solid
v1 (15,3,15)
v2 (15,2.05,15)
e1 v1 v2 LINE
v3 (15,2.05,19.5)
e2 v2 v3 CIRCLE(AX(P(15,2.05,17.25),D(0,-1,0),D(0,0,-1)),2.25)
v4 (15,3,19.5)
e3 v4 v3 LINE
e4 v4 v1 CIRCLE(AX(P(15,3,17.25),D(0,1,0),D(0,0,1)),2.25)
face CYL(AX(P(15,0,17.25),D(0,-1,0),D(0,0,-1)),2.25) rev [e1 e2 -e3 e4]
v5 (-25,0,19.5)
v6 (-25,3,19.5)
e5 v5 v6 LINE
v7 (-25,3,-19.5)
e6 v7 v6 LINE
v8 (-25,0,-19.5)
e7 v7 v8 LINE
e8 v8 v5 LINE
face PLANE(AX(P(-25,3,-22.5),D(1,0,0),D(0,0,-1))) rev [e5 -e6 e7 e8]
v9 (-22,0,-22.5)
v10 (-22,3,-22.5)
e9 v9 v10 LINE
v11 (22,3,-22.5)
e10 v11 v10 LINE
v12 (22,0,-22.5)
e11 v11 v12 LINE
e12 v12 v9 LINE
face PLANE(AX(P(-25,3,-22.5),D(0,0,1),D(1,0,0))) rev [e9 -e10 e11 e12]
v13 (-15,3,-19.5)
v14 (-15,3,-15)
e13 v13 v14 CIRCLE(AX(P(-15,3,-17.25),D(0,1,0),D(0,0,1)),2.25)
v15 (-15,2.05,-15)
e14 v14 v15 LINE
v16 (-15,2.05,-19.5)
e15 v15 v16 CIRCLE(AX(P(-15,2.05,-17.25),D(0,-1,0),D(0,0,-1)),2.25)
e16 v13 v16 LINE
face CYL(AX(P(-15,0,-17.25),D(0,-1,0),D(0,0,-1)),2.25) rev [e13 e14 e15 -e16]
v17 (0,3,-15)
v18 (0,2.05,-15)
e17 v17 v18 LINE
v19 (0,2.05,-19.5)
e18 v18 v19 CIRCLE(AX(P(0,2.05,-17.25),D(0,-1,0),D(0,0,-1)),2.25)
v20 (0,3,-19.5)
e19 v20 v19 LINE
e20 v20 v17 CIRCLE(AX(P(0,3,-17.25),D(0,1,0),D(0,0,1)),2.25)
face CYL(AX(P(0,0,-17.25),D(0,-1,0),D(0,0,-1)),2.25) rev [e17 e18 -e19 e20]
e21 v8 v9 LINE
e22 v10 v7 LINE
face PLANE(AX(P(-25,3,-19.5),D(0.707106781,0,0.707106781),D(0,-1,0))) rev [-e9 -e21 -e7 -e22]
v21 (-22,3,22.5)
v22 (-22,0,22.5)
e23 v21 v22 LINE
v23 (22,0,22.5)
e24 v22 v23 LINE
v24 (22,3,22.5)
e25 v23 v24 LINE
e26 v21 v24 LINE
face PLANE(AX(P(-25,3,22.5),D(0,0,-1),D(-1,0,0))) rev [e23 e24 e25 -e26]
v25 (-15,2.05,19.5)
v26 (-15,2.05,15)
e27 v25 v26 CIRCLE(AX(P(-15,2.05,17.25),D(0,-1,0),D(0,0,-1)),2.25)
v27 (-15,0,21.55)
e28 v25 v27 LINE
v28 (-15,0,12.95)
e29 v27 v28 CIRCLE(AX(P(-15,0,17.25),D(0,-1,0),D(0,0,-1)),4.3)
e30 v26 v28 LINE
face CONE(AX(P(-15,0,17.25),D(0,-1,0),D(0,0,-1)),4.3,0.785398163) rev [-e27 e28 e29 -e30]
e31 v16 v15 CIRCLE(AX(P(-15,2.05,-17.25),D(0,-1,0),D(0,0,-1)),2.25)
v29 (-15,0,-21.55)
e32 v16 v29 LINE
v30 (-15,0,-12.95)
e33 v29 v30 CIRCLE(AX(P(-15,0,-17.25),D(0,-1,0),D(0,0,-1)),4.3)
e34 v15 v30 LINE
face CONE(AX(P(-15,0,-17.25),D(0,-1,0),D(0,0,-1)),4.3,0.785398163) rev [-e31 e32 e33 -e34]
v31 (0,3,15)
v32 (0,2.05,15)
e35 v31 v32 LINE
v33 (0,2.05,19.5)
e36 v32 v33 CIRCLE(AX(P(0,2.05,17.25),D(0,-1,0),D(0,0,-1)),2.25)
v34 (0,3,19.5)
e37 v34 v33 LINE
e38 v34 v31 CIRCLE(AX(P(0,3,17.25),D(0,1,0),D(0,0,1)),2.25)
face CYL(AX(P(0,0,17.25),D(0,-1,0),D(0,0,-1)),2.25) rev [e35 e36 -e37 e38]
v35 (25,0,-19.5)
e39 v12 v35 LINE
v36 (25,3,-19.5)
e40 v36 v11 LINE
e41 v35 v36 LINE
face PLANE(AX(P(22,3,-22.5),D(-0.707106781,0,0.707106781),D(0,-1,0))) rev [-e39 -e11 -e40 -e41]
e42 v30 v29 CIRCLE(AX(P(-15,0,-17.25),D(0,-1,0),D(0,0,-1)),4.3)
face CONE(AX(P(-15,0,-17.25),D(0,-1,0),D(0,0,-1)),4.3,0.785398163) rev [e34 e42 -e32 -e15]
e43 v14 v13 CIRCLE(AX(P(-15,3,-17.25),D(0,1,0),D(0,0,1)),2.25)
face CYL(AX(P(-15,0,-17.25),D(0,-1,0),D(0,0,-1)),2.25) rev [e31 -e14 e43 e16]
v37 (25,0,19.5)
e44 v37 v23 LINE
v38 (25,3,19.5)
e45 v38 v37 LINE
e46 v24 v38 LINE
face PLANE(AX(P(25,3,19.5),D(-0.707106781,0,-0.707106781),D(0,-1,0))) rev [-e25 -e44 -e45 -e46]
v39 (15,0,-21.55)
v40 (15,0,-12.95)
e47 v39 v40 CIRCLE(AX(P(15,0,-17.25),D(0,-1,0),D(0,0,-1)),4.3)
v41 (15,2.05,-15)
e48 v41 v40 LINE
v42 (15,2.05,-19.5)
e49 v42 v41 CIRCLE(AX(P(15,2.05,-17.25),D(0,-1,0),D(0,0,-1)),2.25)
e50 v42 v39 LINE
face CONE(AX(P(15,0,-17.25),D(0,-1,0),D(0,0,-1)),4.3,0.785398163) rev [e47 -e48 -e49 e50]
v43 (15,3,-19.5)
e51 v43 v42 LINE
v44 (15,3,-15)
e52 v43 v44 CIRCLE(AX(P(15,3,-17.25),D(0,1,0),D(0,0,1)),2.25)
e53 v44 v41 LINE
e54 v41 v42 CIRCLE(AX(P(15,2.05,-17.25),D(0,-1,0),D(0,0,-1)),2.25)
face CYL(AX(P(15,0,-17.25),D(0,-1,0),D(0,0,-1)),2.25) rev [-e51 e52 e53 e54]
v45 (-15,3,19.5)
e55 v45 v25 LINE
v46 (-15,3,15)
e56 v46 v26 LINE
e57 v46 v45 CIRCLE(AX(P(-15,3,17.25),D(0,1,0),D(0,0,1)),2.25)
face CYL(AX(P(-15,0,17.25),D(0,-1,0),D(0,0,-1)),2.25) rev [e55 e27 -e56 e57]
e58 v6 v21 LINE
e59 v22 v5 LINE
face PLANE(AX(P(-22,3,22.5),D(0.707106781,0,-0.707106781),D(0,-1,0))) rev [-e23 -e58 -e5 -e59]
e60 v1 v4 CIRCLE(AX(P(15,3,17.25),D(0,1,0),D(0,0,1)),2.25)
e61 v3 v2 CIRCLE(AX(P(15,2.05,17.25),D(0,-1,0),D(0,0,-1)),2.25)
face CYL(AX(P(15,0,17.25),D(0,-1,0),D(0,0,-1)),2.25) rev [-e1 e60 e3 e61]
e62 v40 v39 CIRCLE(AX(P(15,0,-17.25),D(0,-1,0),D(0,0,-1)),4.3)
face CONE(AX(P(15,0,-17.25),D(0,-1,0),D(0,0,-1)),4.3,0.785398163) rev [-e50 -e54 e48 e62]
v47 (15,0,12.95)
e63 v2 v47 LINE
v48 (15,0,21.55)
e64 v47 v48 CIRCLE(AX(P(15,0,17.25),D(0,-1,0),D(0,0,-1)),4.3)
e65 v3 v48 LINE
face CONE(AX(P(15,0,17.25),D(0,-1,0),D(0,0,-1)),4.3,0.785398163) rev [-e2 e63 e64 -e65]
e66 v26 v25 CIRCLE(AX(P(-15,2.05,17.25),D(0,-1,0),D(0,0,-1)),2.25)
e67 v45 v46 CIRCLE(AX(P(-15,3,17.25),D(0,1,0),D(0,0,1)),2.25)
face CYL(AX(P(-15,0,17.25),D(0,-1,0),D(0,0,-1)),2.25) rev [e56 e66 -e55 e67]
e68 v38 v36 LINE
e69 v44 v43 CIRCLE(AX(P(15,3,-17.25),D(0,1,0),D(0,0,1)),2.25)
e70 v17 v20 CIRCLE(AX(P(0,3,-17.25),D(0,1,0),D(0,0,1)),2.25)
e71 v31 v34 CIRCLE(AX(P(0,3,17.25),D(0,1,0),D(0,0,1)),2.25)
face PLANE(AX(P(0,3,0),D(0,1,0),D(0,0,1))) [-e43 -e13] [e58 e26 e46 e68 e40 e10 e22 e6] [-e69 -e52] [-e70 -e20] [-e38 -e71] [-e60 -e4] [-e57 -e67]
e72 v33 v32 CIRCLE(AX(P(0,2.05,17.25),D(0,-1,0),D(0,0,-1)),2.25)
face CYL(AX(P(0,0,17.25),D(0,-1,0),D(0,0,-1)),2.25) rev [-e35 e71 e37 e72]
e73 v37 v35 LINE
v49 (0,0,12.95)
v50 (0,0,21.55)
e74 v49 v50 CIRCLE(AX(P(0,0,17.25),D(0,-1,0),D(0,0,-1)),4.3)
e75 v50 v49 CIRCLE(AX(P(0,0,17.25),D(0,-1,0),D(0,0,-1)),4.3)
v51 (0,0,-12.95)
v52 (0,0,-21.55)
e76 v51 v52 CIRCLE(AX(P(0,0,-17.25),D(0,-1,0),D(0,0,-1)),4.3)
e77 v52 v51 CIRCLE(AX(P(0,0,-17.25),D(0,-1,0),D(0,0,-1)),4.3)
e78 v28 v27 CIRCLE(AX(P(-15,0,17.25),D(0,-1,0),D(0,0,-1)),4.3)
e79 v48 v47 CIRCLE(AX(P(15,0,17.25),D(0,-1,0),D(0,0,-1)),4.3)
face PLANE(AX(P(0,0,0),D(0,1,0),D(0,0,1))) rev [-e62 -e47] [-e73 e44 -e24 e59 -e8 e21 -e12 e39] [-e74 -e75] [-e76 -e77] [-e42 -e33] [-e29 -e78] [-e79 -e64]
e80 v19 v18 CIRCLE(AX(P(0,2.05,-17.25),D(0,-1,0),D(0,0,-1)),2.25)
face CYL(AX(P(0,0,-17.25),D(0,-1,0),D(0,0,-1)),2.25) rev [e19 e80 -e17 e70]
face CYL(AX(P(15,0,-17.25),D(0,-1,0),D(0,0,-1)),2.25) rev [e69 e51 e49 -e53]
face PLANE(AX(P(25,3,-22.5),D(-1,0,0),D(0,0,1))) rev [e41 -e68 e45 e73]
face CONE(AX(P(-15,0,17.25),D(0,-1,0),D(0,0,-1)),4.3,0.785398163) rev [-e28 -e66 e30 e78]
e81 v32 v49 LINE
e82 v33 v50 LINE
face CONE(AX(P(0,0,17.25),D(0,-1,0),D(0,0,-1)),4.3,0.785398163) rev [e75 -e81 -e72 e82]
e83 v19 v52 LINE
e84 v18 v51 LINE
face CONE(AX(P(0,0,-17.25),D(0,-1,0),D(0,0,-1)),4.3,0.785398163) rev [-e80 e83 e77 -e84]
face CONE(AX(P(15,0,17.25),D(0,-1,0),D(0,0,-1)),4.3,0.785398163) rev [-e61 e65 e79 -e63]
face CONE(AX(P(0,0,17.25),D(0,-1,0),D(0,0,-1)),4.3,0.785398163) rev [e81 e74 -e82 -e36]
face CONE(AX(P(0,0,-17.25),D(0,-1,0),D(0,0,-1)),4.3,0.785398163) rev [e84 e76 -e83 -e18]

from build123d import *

# Parameters (mm, degrees)
SKETCH_1_W                = 50
SKETCH_1_H                = 45
EXTRUDE_1_DEPTH           = 3
HOLE_WIZARD_1_D           = 4.5
HOLE_WIZARD_1_DEPTH       = 12.4
HOLE_WIZARD_1_CSINK_D     = 8.6
HOLE_WIZARD_1_CSINK_ANGLE = 90
HOLE_WIZARD_1_TIP         = 1.351936393
CHAMFER_1_SIZE            = 3


with BuildPart() as part:
    # 草图1 → 凸台-拉伸1 (new body)
    with BuildSketch(Plane(origin=(0, 0, 0), x_dir=(1, 0, 0), z_dir=(0, 1, 0))):
        Rectangle(SKETCH_1_W, SKETCH_1_H)
    extrude(amount=EXTRUDE_1_DEPTH)

    # 打孔尺寸(%根据)开槽半沉头木螺钉的类型1
    with Locations(Plane(origin=(0, 0, 0), x_dir=(-1, 0, 0), z_dir=(0, -1, 0))):
        with Locations((15, 17.25), (0, 17.25), (-15, 17.25), (-15, -17.25), (0, -17.25), (15, -17.25)):
            CounterSinkHole(HOLE_WIZARD_1_D / 2, HOLE_WIZARD_1_CSINK_D / 2, depth=HOLE_WIZARD_1_DEPTH, counter_sink_angle=HOLE_WIZARD_1_CSINK_ANGLE)
            with Locations((0, 0, -(HOLE_WIZARD_1_DEPTH + HOLE_WIZARD_1_TIP / 2))):  # 118° drill point
                Cone(0, HOLE_WIZARD_1_D / 2, HOLE_WIZARD_1_TIP, mode=Mode.SUBTRACT)

    # 倒角1
    chamfer_1_edges = [part.edges().sort_by_distance(p)[0] for p in [
        (25, 1.5, 22.5),
        (-25, 1.5, 22.5),
        (-25, 1.5, -22.5),
        (25, 1.5, -22.5),
    ]]
    chamfer(chamfer_1_edges, length=CHAMFER_1_SIZE)


solid = part.part
